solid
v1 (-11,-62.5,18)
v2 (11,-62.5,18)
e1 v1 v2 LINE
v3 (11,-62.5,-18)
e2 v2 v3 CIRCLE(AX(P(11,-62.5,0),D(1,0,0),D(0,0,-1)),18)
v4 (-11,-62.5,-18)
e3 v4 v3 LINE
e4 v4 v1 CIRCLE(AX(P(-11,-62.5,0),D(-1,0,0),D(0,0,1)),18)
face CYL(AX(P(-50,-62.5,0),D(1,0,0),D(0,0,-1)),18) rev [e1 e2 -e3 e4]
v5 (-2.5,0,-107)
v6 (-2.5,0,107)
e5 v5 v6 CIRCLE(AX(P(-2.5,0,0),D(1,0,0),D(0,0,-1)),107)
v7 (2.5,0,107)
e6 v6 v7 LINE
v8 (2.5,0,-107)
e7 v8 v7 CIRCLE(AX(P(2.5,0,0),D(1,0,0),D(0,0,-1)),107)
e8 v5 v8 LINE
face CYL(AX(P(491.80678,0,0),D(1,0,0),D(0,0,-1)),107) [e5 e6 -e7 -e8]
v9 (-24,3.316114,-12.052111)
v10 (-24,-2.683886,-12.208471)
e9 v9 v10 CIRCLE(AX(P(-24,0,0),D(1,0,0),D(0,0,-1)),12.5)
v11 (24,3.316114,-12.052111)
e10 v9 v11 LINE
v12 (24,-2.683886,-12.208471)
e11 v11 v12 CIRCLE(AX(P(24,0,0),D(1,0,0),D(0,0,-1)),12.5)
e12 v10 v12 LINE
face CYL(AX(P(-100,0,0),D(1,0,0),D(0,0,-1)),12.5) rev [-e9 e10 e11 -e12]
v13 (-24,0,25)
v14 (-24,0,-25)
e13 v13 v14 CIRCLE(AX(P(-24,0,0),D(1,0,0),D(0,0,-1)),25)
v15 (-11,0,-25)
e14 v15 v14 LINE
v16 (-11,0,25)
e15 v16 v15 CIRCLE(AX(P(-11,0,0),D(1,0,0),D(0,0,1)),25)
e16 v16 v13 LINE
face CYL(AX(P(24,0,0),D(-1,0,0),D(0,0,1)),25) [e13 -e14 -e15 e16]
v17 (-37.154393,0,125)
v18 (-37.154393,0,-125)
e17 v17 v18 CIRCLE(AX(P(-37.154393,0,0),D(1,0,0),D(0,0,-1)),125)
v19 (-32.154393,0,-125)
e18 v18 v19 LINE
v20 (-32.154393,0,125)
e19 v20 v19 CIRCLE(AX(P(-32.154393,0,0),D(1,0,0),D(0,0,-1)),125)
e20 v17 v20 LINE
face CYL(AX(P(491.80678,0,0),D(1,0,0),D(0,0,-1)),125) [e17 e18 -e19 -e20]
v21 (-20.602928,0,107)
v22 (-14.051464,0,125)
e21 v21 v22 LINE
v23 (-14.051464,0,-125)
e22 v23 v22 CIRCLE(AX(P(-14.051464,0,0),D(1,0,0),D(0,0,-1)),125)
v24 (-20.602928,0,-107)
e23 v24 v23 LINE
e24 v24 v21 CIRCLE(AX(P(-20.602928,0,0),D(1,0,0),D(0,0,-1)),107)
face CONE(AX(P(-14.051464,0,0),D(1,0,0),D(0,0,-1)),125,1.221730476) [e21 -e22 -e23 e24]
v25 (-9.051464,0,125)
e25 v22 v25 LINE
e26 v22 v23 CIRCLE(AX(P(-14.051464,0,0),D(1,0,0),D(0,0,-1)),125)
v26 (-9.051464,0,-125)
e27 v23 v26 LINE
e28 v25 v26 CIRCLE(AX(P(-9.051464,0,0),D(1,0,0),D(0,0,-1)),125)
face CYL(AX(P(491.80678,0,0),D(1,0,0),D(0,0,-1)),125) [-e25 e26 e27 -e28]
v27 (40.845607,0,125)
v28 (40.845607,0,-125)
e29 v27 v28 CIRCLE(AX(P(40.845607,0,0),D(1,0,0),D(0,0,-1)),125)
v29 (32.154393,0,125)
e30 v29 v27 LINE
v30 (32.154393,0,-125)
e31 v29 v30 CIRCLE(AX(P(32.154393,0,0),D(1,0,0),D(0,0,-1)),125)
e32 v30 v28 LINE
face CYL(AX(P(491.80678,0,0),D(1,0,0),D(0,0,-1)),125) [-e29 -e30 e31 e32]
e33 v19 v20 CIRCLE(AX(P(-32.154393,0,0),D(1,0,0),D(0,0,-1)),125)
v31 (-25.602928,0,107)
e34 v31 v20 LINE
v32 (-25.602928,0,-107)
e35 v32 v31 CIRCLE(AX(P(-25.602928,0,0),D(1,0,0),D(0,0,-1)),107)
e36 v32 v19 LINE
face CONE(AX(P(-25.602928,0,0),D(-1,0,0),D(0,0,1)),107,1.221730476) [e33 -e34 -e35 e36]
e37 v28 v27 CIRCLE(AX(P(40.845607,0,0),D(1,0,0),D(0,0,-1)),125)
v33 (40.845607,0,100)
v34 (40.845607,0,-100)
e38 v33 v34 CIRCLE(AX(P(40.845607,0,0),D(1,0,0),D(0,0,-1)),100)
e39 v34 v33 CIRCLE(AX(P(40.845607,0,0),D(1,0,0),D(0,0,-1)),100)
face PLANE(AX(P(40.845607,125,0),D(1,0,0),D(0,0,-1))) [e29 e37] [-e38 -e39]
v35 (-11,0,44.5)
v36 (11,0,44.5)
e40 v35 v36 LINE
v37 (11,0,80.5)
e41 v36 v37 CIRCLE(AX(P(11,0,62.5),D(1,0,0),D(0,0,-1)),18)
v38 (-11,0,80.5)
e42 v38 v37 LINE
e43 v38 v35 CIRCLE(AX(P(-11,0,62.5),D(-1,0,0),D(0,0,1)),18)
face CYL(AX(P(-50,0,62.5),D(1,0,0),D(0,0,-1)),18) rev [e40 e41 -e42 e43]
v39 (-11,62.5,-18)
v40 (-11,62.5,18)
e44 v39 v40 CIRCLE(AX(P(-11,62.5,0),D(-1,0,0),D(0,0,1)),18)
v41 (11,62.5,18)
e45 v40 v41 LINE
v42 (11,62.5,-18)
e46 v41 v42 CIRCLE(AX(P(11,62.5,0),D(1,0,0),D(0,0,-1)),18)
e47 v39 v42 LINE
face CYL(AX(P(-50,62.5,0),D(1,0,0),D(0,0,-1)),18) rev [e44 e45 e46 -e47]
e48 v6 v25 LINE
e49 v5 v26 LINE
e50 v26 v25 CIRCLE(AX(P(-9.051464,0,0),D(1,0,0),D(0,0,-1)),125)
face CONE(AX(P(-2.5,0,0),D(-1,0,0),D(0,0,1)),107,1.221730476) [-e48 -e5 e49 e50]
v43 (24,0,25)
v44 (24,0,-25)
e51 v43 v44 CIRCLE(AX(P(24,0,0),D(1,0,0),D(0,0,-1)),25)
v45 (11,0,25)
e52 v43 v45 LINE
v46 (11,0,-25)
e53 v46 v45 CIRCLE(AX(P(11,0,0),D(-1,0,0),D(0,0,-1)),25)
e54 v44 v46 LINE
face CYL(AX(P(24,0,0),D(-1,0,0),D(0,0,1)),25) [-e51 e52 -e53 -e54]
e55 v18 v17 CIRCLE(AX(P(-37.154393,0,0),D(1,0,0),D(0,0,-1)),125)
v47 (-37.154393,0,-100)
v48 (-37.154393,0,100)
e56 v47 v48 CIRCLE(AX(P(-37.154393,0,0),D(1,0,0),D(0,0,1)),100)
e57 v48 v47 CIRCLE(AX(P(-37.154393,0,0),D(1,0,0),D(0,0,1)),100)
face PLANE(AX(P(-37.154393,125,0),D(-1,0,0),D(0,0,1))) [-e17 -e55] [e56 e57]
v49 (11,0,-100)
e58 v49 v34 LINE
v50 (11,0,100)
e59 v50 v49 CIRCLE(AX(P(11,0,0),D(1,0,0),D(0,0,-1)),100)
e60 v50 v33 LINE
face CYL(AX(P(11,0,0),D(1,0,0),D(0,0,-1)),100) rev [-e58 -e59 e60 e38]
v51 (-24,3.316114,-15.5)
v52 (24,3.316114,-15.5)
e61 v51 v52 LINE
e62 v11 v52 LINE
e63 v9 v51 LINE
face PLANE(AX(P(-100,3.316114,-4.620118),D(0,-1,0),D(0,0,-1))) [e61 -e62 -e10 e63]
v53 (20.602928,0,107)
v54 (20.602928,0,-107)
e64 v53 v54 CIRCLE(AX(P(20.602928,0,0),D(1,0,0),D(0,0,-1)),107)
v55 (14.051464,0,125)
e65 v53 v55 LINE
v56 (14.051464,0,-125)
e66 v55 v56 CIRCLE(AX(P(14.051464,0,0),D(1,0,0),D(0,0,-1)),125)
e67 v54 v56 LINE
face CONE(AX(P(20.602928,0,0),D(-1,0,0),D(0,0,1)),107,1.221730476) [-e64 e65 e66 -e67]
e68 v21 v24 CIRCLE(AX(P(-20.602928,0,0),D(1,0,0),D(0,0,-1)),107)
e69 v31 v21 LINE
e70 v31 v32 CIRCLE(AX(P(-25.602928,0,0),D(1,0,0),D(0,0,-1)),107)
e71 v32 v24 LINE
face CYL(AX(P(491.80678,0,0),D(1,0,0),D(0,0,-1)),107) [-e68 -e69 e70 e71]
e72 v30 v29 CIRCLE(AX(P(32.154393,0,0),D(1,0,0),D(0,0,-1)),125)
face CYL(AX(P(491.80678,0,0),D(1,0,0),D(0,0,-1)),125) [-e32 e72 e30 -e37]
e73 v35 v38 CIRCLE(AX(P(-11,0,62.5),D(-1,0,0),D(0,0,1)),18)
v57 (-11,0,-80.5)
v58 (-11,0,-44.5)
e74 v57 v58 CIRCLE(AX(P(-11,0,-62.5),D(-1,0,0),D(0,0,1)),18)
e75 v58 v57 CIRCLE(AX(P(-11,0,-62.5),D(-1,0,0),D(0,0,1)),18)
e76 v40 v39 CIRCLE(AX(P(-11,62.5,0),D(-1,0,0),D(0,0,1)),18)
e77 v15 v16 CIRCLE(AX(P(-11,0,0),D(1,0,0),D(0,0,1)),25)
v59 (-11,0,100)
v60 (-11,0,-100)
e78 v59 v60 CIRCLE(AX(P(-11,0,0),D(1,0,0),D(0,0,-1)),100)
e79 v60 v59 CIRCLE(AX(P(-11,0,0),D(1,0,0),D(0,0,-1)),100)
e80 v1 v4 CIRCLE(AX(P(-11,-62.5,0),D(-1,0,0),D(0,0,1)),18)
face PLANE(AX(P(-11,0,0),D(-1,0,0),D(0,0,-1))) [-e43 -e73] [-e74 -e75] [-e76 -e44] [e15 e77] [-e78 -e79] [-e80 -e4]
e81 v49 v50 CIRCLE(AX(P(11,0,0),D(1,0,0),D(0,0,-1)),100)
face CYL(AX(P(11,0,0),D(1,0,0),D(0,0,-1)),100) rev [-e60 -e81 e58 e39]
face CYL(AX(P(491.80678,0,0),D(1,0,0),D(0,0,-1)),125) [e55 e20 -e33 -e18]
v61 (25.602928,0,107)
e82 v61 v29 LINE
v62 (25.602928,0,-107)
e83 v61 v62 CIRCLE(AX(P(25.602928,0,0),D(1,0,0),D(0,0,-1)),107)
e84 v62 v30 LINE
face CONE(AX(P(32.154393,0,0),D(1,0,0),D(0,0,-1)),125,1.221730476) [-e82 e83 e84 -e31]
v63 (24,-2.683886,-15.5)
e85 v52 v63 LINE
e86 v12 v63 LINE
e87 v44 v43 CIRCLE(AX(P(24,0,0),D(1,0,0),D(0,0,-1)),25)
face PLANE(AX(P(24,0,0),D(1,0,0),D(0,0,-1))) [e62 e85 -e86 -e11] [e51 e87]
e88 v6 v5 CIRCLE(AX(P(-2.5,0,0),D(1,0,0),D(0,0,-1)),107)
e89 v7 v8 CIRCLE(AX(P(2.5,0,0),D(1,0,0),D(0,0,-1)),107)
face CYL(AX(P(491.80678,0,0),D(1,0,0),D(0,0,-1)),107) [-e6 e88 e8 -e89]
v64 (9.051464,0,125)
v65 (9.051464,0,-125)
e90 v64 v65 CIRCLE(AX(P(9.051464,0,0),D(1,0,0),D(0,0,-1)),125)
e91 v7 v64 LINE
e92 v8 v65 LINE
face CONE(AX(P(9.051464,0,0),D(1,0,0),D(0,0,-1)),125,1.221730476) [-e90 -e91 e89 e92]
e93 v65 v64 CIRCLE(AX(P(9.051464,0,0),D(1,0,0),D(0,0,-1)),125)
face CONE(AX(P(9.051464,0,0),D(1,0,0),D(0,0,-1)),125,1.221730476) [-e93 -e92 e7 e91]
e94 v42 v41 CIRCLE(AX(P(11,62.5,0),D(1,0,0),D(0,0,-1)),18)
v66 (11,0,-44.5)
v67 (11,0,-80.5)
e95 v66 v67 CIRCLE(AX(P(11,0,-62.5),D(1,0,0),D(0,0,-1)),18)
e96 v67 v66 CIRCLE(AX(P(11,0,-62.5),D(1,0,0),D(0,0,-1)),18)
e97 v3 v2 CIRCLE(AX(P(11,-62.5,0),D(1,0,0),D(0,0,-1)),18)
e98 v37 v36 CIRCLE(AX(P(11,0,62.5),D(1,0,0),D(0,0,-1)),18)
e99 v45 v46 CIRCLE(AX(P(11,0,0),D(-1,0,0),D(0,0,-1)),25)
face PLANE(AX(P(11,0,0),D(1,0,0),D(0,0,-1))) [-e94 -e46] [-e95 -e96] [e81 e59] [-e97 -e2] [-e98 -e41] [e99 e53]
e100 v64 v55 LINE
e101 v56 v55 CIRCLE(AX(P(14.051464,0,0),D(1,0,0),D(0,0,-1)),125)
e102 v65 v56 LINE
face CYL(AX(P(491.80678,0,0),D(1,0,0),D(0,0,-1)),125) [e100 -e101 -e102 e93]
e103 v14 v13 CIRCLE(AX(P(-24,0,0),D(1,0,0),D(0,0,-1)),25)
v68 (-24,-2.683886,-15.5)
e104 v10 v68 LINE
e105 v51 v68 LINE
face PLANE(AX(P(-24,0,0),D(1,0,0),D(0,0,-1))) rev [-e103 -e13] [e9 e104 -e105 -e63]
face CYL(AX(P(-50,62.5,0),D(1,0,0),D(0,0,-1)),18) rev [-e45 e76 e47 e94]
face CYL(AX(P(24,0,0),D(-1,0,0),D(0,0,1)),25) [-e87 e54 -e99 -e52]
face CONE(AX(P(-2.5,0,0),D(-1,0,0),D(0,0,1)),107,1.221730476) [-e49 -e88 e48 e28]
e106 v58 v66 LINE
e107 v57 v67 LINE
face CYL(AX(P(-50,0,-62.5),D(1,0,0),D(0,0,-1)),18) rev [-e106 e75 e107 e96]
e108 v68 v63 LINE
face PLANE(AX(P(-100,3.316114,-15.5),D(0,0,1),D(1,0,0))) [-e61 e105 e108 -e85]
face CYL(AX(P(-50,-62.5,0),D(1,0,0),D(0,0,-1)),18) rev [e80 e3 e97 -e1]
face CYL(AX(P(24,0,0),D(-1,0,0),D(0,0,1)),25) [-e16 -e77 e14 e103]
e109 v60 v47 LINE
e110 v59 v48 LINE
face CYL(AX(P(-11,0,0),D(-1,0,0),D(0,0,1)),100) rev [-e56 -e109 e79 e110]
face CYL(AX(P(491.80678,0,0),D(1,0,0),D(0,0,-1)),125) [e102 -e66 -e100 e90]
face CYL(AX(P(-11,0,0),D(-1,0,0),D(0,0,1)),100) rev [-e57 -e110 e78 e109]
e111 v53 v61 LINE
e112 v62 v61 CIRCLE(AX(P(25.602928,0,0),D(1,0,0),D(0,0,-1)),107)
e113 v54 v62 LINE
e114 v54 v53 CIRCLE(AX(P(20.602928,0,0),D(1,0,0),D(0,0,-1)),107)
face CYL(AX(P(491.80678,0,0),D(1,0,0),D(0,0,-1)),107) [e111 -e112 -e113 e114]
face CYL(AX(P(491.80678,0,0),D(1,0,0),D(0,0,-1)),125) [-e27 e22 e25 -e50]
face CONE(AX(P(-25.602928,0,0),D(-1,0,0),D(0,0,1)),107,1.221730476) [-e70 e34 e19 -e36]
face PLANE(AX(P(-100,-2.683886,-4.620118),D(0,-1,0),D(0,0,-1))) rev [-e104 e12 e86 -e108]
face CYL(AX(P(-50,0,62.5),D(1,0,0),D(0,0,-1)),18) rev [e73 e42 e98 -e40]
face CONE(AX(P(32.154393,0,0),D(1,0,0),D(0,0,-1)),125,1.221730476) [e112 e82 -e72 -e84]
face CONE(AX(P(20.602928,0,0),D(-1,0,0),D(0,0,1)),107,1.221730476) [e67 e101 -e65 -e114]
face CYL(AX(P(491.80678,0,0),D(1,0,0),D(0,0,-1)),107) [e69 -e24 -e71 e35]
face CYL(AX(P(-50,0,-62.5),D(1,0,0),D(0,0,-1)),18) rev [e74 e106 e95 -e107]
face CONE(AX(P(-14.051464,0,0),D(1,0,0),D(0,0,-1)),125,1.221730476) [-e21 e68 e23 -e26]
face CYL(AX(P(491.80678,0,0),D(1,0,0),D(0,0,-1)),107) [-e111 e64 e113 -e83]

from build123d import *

# Parameters (mm, degrees)
WEB_START                    = 111
WEB_RECESS_SKETCH_R          = 100
WEB_RECESS_DEPTH             = 100
LIGHTENING_HOLES_SKETCH_R    = 18
LIGHTENING_HOLES_4X_36_DEPTH = 50
HUB_SKETCH_R                 = 25
HUB_50_DEPTH                 = 24
BORE_KEYWAY_SKETCH_R         = 12.5
BORE_KEYWAY_SKETCH_W         = 10.879881684
BORE_KEYWAY_SKETCH_H         = 6
BORE_25_WITH_KEYWAY_DEPTH    = 100


with BuildPart() as part:
    # Pulley Profile Sketch → Pulley Body 3-Groove (revolve)
    with BuildSketch(Plane.XY, mode=Mode.PRIVATE) as pulley_body_3_groove_sk:
        Polygon((-2.5, 107), (2.5, 107), (9.051464217, 125), (14.051464217, 125), (20.602928434, 107), (25.602928434, 107), (32.15439265, 125), (40.84560735, 125), (40.84560735, 12.5), (-37.15439265, 12.5), (-37.15439265, 125), (-32.15439265, 125), (-25.602928434, 107), (-20.602928434, 107), (-14.051464217, 125), (-9.051464217, 125), align=None)
    revolve(pulley_body_3_groove_sk.sketch.rotate(Axis((491.806779687, 0, 0), (-1, 0, 0)), 90), axis=Axis((491.806779687, 0, 0), (-1, 0, 0)))

    # Web Recess Sketch → Web Recess (cut)
    with BuildSketch(Plane(origin=(0, 0, 0), x_dir=(0, 0, -1), z_dir=(1, 0, 0)).offset(WEB_START)):
        Circle(WEB_RECESS_SKETCH_R)
    web_recess = extrude(amount=-WEB_RECESS_DEPTH, mode=Mode.SUBTRACT)

    # Web Recess Mirror: Web Recess across plane
    add(web_recess.mirror(Plane(origin=(0, 0, 0), x_dir=(0, 0, 1), z_dir=(1, 0, 0))), mode=Mode.SUBTRACT)

    # Lightening Holes Sketch → Lightening Holes 4xØ36 (cut, symmetric)
    with BuildSketch(Plane(origin=(0, 0, 0), x_dir=(0, 0, -1), z_dir=(1, 0, 0))):
        with Locations((62.5, 0)):
            Circle(LIGHTENING_HOLES_SKETCH_R)
        with Locations((0, -62.5)):
            Circle(LIGHTENING_HOLES_SKETCH_R)
        with Locations((-62.5, 0)):
            Circle(LIGHTENING_HOLES_SKETCH_R)
        with Locations((0, 62.5)):
            Circle(LIGHTENING_HOLES_SKETCH_R)
    extrude(amount=LIGHTENING_HOLES_4X_36_DEPTH, both=True, mode=Mode.SUBTRACT)

    # Hub Sketch → Hub Ø50 (add, symmetric)
    with BuildSketch(Plane(origin=(0, 0, 0), x_dir=(0, 0, -1), z_dir=(1, 0, 0))):
        with Locations(Location((0, 0, 0), (0, 0, 180))):
            Circle(HUB_SKETCH_R)
    extrude(amount=HUB_50_DEPTH, both=True)

    # Bore Keyway Sketch → Bore Ø25 with Keyway (cut, symmetric)
    with BuildSketch(Plane(origin=(0, 0, 0), x_dir=(0, 0, -1), z_dir=(1, 0, 0))):
        Circle(BORE_KEYWAY_SKETCH_R)
        with Locations((10.060059158, 0.316113857)):
            Rectangle(BORE_KEYWAY_SKETCH_W, BORE_KEYWAY_SKETCH_H)
    extrude(amount=BORE_25_WITH_KEYWAY_DEPTH, both=True, mode=Mode.SUBTRACT)


solid = part.part
